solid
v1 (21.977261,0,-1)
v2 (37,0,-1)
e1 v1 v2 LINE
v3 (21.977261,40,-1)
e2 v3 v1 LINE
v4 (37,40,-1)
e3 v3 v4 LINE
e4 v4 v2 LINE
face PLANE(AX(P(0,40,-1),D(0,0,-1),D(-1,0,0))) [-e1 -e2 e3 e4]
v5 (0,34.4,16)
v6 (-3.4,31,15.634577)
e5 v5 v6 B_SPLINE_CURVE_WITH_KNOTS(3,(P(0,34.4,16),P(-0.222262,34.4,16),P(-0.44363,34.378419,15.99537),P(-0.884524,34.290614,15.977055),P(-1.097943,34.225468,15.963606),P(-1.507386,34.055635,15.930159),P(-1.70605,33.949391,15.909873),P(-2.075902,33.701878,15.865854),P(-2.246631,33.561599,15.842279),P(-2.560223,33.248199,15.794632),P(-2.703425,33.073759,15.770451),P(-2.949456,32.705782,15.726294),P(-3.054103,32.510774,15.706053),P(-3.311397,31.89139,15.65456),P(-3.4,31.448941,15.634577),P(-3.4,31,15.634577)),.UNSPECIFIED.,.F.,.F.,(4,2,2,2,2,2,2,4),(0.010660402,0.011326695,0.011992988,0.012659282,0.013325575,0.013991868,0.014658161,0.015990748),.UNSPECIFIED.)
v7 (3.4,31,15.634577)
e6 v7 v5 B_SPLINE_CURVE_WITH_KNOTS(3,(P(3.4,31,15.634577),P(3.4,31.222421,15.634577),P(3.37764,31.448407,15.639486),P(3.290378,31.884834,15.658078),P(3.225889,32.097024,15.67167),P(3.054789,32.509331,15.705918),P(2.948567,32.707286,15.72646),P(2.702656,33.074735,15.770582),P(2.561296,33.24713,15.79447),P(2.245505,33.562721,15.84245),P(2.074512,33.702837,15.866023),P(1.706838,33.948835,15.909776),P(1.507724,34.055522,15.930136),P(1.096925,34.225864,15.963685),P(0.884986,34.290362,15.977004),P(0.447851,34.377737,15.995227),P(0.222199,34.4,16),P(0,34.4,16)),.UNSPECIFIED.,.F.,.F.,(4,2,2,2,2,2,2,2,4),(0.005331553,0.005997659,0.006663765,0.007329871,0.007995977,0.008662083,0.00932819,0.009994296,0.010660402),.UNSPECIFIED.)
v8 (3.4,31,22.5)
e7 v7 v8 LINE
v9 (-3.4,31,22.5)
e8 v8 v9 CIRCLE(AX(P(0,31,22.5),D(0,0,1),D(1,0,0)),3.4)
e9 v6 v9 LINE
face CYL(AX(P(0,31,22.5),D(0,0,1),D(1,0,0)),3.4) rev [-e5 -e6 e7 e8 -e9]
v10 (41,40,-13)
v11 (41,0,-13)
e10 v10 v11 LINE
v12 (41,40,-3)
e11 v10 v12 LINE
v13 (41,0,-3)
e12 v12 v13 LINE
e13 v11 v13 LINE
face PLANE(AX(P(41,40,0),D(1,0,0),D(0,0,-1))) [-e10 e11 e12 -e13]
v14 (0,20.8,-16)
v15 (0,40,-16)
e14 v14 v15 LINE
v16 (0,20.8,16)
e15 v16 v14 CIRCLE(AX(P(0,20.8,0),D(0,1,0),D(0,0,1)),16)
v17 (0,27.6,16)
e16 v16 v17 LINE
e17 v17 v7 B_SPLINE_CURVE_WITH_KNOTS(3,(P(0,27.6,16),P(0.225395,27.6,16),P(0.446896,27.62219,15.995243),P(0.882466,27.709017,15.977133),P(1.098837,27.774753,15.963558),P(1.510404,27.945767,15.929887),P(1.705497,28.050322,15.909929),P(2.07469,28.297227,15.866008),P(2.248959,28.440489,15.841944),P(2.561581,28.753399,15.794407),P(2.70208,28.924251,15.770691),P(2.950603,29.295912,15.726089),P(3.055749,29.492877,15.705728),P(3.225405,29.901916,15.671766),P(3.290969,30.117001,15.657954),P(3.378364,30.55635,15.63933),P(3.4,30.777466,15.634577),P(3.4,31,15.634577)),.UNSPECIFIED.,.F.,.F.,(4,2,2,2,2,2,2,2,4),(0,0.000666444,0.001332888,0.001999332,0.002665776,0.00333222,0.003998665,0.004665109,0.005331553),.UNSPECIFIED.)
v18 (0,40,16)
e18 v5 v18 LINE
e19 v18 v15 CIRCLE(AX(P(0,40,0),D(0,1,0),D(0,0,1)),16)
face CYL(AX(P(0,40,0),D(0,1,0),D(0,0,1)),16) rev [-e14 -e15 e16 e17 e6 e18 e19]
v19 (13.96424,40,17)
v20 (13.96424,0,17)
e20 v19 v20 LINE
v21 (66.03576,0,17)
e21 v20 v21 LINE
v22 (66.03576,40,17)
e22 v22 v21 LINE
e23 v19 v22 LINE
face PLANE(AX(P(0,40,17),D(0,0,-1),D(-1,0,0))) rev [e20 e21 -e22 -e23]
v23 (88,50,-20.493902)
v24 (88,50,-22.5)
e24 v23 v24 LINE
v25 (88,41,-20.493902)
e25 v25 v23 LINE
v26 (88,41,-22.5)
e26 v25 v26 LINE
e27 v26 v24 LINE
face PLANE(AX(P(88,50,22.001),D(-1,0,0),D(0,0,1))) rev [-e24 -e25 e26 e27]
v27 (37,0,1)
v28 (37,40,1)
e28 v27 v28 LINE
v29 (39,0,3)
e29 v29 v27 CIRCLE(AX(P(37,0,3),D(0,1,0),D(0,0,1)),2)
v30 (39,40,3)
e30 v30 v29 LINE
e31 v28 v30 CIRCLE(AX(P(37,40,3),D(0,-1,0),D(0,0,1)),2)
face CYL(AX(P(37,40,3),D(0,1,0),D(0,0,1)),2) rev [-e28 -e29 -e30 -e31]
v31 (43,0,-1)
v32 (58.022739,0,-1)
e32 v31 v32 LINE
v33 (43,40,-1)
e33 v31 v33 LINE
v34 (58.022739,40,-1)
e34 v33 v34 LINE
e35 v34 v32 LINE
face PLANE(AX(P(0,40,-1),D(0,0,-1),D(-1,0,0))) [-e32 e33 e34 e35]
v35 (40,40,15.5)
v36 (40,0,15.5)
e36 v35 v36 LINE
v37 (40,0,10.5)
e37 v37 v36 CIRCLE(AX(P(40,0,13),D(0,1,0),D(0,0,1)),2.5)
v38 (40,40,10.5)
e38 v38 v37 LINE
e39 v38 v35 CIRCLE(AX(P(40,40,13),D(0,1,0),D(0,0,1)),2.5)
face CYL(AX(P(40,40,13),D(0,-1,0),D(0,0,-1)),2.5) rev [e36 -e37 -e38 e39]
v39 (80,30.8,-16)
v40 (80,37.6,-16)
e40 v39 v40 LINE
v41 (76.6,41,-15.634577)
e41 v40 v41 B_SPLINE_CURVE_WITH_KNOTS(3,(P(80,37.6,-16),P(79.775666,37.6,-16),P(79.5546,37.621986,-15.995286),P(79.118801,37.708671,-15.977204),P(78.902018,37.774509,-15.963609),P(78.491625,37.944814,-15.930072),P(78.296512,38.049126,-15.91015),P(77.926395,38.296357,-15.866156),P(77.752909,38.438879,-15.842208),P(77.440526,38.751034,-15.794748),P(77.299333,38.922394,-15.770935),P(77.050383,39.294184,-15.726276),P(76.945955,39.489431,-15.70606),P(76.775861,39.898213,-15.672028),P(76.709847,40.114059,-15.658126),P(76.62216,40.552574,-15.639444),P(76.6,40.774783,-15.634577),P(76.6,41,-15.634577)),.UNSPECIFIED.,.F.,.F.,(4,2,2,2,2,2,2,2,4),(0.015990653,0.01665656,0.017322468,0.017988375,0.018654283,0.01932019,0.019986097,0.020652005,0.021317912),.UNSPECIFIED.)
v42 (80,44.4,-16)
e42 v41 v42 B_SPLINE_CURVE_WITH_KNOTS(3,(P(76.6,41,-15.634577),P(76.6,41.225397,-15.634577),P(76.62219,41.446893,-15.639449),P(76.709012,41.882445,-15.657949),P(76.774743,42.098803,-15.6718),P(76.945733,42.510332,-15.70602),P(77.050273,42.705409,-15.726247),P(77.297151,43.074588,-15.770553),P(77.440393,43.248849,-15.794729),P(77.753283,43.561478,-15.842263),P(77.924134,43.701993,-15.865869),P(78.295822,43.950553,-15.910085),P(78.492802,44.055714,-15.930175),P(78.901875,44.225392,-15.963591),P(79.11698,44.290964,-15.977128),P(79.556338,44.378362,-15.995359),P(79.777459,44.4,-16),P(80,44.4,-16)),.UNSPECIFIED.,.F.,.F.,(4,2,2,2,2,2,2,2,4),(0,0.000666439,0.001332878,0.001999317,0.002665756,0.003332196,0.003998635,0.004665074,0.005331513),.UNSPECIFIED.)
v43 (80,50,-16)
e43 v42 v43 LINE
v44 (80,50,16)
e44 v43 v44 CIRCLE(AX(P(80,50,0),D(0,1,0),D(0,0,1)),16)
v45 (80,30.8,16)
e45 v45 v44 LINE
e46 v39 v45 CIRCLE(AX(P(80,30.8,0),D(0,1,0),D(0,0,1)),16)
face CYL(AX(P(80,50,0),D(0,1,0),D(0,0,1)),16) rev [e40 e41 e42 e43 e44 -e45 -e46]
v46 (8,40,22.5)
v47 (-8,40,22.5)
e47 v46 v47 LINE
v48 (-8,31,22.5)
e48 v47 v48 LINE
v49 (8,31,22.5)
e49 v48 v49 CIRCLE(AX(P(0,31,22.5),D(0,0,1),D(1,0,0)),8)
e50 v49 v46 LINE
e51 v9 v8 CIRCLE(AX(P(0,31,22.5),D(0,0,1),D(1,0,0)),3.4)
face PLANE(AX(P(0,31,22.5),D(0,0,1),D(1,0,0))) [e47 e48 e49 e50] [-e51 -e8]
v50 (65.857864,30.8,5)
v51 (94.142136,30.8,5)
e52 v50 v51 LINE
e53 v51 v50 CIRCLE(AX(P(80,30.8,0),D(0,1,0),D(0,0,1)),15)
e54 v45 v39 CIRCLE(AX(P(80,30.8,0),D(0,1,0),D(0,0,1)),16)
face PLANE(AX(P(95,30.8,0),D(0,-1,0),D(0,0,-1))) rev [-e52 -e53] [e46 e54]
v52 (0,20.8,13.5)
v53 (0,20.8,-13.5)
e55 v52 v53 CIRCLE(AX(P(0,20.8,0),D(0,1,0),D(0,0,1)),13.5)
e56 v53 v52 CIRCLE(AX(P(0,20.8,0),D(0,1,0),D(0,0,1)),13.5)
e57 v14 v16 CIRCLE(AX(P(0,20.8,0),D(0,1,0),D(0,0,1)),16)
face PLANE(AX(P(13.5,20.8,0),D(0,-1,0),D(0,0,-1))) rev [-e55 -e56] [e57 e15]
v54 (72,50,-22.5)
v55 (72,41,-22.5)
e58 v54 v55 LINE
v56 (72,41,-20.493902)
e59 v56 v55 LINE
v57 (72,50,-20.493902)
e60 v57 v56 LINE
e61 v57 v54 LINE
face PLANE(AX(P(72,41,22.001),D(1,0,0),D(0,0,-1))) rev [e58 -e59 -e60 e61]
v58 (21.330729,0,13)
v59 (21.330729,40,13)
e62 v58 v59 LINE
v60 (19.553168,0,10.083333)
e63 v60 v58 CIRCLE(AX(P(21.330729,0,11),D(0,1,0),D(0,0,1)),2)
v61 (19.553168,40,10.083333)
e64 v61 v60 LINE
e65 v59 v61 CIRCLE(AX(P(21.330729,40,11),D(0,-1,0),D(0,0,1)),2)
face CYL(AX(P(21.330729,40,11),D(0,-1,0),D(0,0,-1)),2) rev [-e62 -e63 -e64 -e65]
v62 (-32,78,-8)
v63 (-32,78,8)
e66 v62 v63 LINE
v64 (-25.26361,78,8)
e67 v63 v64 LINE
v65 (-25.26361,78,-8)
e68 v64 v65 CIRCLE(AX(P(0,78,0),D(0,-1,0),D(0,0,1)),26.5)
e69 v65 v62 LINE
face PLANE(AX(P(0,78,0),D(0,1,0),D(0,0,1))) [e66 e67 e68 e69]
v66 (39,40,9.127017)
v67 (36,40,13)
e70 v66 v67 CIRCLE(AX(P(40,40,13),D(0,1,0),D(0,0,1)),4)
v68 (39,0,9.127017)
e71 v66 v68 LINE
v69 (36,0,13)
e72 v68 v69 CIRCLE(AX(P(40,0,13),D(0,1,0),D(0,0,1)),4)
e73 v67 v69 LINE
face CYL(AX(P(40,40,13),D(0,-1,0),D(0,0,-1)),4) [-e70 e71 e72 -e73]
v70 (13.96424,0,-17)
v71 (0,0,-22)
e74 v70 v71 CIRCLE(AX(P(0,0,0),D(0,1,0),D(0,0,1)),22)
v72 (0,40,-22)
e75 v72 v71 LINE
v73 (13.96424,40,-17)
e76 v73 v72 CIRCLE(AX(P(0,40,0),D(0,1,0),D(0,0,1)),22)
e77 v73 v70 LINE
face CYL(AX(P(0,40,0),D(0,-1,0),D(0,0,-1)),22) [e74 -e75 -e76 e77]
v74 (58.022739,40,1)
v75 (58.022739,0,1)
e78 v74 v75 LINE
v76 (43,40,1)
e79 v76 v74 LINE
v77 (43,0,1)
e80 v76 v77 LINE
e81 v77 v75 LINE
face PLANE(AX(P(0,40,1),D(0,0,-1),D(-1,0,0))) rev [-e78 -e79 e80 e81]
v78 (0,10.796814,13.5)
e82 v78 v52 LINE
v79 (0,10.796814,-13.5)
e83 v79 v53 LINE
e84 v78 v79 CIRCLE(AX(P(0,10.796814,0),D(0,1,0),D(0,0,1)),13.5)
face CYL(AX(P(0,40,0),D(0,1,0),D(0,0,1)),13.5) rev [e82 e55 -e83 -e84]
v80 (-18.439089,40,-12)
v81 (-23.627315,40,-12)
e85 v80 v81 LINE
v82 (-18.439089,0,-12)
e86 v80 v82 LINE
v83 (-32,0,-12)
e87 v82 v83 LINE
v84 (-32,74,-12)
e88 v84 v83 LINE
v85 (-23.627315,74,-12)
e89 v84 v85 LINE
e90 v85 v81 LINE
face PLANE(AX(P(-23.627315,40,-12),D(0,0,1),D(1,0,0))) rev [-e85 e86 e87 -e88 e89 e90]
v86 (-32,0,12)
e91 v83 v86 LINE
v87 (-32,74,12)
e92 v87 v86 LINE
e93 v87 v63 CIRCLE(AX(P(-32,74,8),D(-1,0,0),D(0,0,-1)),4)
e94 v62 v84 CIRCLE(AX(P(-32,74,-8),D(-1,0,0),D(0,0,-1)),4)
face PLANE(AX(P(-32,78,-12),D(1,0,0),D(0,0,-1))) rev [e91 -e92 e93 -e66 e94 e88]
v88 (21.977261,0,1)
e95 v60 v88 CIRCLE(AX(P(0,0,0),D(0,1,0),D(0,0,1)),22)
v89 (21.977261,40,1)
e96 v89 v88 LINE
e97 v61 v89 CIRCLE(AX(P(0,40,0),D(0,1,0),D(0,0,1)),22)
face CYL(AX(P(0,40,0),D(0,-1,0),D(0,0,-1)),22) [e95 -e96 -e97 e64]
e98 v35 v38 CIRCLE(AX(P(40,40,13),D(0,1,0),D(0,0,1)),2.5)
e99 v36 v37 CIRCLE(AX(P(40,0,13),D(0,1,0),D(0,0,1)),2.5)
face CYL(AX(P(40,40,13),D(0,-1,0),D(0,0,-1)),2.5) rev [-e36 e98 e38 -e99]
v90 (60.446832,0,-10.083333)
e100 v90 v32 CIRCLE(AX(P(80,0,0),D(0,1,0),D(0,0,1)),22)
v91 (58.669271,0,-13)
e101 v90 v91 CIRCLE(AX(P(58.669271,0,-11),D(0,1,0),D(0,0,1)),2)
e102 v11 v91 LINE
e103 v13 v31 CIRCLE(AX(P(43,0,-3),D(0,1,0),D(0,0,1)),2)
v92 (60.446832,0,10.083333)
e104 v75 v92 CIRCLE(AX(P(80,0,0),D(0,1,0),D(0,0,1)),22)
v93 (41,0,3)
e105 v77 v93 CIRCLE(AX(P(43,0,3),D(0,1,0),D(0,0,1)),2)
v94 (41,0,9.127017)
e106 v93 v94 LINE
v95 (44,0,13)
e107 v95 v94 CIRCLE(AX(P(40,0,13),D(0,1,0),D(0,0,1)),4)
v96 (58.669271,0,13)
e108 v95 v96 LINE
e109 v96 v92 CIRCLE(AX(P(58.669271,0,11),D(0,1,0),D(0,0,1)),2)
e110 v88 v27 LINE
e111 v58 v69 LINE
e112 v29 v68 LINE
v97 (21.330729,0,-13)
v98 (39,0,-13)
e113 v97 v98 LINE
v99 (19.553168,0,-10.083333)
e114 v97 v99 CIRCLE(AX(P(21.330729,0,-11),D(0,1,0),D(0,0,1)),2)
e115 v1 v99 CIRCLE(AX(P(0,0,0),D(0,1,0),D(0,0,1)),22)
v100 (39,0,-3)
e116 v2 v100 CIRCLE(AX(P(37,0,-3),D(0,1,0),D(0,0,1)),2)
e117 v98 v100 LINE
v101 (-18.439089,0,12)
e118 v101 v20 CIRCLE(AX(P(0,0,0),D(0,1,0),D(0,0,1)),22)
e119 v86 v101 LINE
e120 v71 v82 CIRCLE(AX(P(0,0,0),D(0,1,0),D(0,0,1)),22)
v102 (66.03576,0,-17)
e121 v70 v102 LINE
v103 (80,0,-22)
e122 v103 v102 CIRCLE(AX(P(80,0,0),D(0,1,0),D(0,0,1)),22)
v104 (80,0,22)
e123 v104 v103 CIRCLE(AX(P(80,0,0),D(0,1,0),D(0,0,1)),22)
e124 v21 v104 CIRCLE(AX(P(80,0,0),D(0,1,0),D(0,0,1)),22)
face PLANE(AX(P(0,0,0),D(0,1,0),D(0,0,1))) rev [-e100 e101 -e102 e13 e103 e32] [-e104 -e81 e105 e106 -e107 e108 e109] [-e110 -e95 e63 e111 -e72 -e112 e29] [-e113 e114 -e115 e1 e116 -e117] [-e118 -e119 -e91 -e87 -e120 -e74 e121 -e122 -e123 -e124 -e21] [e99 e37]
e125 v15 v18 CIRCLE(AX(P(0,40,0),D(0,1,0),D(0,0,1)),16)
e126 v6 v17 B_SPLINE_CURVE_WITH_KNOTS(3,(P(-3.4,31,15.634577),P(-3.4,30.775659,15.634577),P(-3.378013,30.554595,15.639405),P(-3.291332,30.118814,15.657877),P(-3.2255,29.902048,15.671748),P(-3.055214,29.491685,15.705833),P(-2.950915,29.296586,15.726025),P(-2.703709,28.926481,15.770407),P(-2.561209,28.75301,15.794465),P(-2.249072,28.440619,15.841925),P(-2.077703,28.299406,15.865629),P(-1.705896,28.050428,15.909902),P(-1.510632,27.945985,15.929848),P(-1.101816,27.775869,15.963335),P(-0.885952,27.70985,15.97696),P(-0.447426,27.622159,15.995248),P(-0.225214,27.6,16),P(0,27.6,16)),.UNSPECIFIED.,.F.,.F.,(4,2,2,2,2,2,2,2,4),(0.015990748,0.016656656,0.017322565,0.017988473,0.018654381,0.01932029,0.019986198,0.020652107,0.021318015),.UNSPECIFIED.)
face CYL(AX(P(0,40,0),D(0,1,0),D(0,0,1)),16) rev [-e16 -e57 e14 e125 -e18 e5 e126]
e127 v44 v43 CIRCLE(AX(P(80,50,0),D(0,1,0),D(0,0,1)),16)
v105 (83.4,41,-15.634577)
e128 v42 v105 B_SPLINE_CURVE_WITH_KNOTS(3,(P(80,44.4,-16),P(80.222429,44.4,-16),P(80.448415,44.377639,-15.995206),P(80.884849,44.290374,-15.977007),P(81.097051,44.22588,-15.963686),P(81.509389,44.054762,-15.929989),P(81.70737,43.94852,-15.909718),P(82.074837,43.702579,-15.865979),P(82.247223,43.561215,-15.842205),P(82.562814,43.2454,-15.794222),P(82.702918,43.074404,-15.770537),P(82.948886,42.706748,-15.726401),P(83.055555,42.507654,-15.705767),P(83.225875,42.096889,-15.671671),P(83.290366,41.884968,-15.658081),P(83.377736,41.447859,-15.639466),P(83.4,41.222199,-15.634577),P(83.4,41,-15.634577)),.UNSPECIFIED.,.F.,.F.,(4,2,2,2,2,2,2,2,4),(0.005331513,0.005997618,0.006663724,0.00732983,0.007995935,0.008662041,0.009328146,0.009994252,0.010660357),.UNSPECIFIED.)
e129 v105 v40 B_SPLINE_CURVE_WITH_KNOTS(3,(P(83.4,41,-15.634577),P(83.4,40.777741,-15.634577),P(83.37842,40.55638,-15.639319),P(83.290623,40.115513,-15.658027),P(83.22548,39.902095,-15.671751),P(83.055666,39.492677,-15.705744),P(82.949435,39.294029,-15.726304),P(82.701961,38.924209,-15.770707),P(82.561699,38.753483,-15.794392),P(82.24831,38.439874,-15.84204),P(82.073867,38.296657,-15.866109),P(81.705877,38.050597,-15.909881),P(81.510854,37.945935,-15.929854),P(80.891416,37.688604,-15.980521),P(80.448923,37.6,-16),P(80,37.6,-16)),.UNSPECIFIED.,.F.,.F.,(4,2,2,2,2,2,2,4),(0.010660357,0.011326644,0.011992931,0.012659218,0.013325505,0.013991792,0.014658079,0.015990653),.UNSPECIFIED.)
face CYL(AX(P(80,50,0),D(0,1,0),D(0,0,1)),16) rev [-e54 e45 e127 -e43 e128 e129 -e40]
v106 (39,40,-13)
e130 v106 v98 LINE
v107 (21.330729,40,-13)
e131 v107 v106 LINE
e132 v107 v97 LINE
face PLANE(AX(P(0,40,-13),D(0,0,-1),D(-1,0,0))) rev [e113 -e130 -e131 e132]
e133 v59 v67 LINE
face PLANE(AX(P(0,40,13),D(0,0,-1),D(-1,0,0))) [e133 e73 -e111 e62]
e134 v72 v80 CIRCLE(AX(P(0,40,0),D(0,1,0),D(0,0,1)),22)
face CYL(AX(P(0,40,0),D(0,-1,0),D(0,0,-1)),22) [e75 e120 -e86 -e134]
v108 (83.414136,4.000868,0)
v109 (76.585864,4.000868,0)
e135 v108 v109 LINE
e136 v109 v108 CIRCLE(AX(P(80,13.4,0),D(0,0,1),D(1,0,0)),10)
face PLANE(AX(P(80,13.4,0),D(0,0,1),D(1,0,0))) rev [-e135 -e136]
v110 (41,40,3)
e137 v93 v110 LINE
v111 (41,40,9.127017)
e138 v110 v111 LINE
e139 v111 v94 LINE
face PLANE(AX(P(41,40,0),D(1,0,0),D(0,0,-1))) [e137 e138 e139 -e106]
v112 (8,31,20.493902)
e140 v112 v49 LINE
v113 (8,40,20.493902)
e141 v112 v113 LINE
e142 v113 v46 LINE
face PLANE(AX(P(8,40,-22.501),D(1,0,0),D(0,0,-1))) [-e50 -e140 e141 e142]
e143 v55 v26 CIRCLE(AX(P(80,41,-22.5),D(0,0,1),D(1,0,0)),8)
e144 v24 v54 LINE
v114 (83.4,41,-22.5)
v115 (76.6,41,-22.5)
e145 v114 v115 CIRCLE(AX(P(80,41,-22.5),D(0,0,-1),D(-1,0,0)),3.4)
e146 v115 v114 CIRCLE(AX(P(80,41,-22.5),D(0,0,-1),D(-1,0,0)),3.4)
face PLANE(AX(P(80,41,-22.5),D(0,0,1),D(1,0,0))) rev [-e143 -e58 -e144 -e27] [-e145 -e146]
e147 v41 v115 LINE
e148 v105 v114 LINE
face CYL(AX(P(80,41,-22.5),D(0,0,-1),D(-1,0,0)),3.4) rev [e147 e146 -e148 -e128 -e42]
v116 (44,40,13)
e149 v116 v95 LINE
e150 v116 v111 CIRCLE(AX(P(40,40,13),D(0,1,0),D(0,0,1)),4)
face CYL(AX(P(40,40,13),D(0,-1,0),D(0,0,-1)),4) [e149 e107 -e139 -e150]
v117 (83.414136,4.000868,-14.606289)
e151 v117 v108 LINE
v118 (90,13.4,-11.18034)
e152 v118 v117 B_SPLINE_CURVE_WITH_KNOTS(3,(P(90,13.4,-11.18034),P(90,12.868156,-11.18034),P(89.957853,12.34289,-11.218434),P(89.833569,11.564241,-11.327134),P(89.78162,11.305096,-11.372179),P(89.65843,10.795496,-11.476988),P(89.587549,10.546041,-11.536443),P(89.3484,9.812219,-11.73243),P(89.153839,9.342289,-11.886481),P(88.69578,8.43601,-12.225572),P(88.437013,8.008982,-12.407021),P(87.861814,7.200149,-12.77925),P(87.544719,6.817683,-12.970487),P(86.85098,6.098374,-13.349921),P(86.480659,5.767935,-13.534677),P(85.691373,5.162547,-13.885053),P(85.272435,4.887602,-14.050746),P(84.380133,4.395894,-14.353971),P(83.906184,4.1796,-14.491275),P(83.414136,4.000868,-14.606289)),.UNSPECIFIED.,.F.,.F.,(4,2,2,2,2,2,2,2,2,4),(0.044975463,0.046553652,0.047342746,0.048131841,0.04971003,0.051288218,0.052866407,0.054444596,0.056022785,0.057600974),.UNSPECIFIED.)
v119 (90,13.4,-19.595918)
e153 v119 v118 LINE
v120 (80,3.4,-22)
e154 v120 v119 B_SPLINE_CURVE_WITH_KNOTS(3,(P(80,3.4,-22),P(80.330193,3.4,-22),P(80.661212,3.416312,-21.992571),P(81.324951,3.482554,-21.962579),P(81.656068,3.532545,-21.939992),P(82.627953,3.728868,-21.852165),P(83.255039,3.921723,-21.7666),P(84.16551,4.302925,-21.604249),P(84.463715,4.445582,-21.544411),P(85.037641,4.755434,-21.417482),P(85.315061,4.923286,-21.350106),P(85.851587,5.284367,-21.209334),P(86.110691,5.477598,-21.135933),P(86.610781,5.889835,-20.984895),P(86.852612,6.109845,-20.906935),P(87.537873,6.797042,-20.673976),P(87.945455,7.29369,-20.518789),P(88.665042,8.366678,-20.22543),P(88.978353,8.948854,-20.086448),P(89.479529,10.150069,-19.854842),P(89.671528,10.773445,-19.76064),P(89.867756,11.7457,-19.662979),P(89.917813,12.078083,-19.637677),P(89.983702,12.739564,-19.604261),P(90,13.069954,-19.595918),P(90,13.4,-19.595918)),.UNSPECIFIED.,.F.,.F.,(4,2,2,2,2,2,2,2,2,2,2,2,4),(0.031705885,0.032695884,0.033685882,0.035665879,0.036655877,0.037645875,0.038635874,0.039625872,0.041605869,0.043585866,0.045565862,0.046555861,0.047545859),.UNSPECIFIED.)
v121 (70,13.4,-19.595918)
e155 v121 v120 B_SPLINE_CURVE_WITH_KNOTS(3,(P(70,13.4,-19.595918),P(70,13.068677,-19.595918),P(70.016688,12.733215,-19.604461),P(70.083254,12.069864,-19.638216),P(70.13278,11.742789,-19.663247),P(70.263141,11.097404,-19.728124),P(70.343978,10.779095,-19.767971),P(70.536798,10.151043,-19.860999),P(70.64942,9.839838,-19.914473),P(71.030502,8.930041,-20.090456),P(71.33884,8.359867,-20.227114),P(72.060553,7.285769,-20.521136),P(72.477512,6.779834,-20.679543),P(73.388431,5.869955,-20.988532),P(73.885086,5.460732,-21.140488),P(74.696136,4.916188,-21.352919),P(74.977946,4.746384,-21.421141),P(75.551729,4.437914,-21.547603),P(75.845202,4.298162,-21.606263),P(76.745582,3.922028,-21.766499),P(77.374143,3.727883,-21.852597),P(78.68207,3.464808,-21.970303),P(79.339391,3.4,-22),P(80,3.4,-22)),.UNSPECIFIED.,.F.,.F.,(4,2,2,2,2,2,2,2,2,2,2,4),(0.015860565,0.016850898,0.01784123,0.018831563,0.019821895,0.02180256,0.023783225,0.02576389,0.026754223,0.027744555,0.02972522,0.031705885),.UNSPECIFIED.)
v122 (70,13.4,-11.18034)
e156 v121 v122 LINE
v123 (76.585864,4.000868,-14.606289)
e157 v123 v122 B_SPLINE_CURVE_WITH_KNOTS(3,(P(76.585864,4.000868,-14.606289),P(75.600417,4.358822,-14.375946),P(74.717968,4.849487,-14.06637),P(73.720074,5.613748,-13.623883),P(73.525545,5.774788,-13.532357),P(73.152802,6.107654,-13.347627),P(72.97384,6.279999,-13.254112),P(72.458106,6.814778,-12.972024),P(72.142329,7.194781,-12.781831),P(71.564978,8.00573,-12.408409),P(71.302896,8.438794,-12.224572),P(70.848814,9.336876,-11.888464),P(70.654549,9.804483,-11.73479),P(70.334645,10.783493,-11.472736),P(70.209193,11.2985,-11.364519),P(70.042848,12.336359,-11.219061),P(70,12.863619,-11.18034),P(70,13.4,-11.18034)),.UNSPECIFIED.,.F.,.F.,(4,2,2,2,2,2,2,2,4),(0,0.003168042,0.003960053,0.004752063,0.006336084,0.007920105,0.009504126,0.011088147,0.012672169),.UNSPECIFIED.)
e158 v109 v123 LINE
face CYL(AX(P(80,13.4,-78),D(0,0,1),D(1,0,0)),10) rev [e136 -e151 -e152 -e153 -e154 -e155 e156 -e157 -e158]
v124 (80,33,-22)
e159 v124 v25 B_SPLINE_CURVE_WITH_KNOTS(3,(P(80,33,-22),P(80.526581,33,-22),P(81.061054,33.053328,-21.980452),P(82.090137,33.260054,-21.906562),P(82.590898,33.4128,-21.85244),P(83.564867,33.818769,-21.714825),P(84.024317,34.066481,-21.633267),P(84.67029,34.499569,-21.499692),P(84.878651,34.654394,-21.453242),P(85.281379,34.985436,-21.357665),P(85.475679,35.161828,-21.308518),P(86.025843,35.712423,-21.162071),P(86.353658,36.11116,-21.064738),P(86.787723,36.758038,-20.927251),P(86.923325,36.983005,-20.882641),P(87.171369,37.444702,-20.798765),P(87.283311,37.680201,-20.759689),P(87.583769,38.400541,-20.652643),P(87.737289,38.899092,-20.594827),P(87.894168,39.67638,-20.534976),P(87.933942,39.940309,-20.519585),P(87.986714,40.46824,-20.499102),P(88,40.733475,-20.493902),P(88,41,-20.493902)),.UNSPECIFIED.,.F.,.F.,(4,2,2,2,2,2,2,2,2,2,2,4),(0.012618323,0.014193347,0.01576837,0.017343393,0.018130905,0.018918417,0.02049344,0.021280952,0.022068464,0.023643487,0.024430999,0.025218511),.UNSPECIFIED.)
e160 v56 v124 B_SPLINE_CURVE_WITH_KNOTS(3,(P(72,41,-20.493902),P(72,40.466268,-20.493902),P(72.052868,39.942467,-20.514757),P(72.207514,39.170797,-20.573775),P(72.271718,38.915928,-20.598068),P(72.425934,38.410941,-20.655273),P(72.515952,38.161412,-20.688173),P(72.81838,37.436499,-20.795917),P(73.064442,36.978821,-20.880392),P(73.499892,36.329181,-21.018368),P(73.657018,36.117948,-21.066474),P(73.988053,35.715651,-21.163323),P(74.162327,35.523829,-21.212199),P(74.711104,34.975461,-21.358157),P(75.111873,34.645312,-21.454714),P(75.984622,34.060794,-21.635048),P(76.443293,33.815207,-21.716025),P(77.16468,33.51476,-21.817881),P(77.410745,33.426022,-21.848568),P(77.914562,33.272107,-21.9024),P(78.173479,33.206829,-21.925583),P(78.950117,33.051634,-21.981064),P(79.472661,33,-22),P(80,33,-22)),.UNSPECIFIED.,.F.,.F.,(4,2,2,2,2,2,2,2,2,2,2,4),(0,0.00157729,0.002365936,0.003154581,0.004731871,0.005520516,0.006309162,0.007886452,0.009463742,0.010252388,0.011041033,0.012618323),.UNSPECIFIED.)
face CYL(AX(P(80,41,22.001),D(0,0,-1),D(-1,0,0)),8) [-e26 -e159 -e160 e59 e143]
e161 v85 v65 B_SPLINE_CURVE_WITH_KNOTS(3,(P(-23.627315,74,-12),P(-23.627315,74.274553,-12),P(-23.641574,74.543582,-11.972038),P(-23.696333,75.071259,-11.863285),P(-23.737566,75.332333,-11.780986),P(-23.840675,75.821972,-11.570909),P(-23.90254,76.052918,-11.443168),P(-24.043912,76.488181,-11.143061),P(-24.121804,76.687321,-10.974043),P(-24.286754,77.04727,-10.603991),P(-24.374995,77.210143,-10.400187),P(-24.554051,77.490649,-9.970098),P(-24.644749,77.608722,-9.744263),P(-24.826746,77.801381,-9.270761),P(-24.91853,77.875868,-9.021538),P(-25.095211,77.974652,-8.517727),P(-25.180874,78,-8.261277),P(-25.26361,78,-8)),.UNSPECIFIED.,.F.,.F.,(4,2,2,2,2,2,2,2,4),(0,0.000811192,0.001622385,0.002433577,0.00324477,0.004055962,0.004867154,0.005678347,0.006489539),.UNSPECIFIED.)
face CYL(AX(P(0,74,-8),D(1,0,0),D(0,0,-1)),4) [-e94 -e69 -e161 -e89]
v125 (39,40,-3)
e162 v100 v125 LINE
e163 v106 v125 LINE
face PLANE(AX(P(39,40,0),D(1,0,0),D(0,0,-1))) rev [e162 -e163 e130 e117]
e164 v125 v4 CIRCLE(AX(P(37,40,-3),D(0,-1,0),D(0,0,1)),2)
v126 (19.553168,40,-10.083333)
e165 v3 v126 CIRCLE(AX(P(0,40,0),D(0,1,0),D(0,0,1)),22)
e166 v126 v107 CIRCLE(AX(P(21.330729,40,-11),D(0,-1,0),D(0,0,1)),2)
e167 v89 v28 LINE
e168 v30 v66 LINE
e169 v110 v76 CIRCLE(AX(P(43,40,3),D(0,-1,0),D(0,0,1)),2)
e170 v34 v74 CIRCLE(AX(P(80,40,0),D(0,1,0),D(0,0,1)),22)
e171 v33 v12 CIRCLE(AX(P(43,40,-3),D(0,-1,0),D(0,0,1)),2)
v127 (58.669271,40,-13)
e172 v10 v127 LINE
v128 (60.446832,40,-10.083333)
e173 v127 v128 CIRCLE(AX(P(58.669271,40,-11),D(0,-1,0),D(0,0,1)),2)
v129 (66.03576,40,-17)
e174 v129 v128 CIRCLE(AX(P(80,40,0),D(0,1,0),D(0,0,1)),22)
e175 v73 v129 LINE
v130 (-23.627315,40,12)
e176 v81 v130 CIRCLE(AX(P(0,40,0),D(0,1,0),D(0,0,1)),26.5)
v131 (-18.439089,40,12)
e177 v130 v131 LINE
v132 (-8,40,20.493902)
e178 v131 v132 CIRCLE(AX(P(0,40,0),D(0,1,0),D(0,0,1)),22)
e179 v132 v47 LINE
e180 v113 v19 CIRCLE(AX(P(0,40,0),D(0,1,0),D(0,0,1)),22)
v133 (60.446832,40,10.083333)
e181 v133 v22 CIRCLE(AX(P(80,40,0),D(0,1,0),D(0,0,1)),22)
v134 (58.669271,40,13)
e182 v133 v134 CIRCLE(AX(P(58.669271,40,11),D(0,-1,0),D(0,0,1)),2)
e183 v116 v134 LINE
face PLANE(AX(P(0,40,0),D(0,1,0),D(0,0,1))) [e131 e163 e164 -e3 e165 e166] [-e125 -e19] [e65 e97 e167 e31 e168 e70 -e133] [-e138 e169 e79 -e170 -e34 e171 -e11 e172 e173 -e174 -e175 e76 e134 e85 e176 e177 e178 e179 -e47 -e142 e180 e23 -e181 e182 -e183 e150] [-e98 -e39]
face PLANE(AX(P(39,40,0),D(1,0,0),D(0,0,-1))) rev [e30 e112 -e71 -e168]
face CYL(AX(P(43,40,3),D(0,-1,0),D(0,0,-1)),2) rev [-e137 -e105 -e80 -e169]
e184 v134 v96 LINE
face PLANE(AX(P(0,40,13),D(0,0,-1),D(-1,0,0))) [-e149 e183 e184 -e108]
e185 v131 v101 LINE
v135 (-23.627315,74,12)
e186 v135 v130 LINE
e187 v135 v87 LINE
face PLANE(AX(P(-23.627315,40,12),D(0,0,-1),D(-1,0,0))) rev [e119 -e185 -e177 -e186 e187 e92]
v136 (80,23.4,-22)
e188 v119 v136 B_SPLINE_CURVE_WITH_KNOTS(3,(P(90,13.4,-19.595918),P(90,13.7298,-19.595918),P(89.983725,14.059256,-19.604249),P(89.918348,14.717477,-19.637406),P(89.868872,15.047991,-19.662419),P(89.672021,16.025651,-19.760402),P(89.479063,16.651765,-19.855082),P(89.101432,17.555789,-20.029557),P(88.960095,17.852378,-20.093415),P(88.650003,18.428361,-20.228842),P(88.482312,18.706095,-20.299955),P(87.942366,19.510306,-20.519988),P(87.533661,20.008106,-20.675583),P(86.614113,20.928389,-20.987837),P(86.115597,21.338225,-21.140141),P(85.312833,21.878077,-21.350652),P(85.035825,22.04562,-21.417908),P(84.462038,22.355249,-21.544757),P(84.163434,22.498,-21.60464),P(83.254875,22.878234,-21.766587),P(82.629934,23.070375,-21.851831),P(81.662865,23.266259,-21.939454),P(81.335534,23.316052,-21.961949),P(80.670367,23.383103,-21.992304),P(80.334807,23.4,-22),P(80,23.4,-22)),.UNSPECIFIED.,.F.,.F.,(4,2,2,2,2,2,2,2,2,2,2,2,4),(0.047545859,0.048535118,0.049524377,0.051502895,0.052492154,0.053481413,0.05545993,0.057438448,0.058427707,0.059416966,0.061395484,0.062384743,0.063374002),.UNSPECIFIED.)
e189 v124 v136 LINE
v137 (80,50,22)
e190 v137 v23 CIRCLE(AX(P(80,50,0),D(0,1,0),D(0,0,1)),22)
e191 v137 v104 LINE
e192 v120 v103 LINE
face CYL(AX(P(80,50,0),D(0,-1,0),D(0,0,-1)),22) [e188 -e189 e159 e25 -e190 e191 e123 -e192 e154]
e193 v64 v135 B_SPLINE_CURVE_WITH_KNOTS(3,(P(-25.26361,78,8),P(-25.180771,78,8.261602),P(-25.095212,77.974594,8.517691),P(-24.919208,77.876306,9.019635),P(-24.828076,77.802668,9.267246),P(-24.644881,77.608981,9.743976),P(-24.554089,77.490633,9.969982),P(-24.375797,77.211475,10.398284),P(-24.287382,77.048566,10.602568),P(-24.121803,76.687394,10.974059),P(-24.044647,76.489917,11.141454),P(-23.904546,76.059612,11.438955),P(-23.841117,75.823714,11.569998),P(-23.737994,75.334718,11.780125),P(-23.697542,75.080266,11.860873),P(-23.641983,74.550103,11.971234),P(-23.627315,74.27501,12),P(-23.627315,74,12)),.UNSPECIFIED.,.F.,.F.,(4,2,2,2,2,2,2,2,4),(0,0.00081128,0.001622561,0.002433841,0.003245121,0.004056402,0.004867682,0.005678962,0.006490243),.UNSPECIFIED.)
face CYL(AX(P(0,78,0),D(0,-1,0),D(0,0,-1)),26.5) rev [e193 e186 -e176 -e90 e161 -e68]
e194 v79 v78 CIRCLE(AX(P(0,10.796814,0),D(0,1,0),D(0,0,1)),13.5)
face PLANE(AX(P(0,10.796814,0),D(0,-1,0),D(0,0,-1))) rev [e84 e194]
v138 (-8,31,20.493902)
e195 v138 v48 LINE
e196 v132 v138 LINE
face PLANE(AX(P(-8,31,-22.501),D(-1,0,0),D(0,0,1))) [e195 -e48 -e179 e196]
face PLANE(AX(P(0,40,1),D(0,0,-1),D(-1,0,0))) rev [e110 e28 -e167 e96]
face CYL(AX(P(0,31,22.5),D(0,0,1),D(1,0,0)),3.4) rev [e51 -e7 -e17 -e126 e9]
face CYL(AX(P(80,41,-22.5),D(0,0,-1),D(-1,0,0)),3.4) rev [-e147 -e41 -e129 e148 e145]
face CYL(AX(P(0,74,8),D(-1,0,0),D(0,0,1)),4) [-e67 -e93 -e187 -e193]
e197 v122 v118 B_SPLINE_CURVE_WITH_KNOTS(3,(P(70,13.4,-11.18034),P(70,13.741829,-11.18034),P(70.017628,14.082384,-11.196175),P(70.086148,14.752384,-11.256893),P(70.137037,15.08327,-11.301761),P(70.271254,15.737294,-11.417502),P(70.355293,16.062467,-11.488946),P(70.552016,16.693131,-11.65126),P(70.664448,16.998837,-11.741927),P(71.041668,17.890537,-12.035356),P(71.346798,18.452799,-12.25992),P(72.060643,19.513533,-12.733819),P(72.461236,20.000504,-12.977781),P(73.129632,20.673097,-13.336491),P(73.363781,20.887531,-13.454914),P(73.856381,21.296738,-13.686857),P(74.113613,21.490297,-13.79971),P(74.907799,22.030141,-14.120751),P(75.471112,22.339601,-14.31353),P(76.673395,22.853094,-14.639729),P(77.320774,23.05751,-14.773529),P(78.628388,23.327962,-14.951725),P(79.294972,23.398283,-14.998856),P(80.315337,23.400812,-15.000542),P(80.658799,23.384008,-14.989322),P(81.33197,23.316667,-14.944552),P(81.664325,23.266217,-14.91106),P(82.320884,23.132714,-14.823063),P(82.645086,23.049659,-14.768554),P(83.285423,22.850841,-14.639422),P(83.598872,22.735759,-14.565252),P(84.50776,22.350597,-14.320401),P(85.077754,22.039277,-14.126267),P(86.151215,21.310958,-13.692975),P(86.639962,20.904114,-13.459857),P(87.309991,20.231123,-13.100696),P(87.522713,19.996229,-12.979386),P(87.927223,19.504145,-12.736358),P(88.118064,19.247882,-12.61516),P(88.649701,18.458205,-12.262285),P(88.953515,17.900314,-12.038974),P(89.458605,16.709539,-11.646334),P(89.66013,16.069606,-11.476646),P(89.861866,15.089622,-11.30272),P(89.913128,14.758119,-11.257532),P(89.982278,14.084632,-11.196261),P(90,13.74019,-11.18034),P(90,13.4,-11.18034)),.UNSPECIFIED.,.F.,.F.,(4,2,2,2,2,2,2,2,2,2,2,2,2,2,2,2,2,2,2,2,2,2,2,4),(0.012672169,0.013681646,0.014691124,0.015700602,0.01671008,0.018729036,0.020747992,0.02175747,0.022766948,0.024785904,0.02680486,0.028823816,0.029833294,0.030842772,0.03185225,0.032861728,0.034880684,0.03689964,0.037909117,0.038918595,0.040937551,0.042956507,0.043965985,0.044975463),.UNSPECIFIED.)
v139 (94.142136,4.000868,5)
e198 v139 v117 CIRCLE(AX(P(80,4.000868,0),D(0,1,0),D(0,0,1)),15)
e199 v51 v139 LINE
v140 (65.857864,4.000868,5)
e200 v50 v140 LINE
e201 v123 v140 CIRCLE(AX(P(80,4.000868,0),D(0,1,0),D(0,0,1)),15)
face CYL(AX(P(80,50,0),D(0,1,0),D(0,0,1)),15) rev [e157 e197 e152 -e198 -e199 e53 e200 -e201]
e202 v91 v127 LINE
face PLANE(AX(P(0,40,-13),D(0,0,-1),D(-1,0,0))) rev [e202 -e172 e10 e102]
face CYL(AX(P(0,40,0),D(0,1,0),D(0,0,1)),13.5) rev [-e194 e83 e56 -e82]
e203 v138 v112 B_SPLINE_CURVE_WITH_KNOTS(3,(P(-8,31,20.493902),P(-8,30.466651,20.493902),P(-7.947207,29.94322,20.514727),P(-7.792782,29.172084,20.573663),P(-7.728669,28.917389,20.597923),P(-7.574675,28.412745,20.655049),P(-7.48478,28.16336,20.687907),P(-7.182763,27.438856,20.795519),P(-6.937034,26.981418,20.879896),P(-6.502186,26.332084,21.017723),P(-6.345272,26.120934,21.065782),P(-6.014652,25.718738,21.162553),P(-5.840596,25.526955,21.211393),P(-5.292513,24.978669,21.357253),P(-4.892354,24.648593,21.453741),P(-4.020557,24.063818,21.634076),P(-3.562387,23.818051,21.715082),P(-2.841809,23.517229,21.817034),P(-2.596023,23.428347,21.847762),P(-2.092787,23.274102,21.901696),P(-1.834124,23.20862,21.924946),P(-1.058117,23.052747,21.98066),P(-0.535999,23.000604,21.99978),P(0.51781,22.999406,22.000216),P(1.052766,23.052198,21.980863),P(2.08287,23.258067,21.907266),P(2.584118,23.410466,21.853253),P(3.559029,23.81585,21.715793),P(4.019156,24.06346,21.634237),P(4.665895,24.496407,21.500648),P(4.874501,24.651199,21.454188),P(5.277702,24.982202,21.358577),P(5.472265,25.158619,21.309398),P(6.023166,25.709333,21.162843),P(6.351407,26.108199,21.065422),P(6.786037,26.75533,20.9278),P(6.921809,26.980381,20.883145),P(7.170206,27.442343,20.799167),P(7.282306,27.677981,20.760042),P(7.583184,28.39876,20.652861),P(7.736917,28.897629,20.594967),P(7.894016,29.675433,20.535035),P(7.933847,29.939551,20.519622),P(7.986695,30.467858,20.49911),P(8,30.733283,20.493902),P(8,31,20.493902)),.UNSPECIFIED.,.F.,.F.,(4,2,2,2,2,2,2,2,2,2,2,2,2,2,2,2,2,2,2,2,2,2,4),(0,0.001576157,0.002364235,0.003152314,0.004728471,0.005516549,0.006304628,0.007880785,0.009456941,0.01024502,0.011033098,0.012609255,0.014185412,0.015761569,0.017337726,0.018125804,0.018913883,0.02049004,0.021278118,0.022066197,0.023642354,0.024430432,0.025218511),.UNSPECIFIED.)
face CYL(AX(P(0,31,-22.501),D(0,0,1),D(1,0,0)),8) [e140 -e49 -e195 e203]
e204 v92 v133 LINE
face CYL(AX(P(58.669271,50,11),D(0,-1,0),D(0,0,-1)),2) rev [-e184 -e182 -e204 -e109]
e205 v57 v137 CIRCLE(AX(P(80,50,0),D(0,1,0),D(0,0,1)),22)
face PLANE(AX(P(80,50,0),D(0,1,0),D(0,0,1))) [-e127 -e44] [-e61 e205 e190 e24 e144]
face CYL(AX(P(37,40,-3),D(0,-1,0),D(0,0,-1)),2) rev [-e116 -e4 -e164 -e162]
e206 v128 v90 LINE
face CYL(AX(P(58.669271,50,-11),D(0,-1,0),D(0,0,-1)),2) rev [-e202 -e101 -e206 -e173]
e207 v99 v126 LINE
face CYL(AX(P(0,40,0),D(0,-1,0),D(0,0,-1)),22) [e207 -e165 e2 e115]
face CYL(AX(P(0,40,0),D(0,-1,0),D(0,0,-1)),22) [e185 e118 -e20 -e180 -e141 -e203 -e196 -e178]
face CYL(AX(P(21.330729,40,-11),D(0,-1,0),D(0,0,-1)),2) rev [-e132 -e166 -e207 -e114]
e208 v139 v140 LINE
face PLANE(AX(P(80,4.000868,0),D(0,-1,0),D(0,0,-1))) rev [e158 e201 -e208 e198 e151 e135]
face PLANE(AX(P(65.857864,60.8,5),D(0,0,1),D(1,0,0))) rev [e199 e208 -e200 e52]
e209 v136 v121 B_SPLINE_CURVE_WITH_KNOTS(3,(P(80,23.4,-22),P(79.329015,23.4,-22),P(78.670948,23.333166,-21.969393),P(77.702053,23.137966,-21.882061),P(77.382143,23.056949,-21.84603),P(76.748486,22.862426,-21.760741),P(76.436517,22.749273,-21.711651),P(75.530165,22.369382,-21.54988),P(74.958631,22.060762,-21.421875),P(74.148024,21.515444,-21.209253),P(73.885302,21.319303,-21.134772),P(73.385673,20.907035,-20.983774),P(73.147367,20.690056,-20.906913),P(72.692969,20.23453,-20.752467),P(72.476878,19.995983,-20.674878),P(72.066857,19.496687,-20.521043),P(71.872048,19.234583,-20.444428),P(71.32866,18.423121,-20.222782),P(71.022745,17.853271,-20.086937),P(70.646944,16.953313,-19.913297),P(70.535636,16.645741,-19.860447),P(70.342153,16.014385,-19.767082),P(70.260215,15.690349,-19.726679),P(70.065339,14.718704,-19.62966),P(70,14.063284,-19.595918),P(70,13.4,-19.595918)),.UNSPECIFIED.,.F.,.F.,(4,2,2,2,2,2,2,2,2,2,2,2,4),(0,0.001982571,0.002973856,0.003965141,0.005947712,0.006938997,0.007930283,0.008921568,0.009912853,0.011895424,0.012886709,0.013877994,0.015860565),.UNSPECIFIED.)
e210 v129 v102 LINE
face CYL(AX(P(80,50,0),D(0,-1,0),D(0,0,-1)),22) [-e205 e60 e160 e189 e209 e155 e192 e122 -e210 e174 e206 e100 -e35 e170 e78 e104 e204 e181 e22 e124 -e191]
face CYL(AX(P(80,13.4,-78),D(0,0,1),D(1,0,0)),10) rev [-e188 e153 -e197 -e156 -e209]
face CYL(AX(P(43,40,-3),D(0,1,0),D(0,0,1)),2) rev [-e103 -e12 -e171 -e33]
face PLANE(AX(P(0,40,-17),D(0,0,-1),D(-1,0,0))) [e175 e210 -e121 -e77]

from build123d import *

# Parameters (mm, degrees)
HUB_1_DEPTH                          = 40
HUB_2_SKETCH_R                       = 22
HUB_2_DEPTH                          = 50
RIBBED_WEB_SKETCH_R                  = 2.5
RIBBED_WEB_DEPTH                     = 40
WEB_FILLETS_R2_R                     = 2
HUB_1_BORE_27_CBORE_32_D             = 27
HUB_1_BORE_27_CBORE_32_DEPTH         = 29.20318647
HUB_1_BORE_27_CBORE_32_CBORE_D       = 32
HUB_1_BORE_27_CBORE_32_CBORE_DEPTH   = 19.2
UPRIGHT_TAB_DEPTH                    = 78
TAB_FILLETS_R4_R                     = 4
HUB_2_BORE_30_CBORE_32_D             = 30
HUB_2_BORE_30_CBORE_32_DEPTH         = 45.999131514
HUB_2_BORE_30_CBORE_32_CBORE_D       = 32
HUB_2_BORE_30_CBORE_32_CBORE_DEPTH   = 19.2
CLEARANCE_CUT_SKETCH_R               = 10
CLEARANCE_CUT_DEPTH                  = 78
HUB_2_SET_SCREW_BOSS_REACH           = 137.898
HUB_2_SET_SCREW_BOSS_END_RADIUS      = 22
HUB_1_SET_SCREW_BOSS_REACH           = 138.062
HUB_1_SET_SCREW_BOSS_END_RADIUS      = 22
M8X1_25_TAPPED_HOLE1_REACH           = 129.475
M8X1_25_TAPPED_HOLE1_BORE_R          = 3.4
M8X1_25_TAPPED_HOLE1_ON_FACE_2_REACH = 122.988
M8X1_25_TAPPED_HOLE1_BORE_2_R        = 3.4
WEB_BOSS_DEPTH                       = 26.799131514


with BuildPart() as part:
    # Hub 1 Sketch → Hub 1 (new body)
    with BuildSketch(Plane(origin=(0, 0, 0), x_dir=(1, 0, 0), z_dir=(0, 1, 0))):
        with BuildLine():
            Line((-23.627314701, 12), (-18.439088915, 12))
            ThreePointArc((-18.439088915, 12), (22, 0), (-18.439088915, -12))
            Line((-18.439088915, -12), (-23.627314701, -12))
            ThreePointArc((-23.627314701, -12), (-26.5, 0), (-23.627314701, 12))
        make_face()
    extrude(amount=HUB_1_DEPTH)



with BuildPart() as body_2:
    # Hub 2 Sketch → Hub 2 (new body)
    with BuildSketch(Plane(origin=(0, 0, 0), x_dir=(1, 0, 0), z_dir=(0, 1, 0))):
        with Locations(Location((80, 0, 0), (0, 0, 270))):
            Circle(HUB_2_SKETCH_R)
    extrude(amount=HUB_2_DEPTH)


with BuildPart() as part_1:
    add(part.part)

    add(body_2.part)  # Ribbed Web merges body 2
    # Ribbed Web Sketch → Ribbed Web (add)
    with BuildSketch(Plane(origin=(0, 0, 0), x_dir=(1, 0, 0), z_dir=(0, 1, 0))):
        with BuildLine():
            Line((39, -1), (39, -9.127016654))
            ThreePointArc((39, -9.127016654), (36.83772234, -10.550510257), (36, -13))
            Line((36, -13), (17.748239349, -13))
            ThreePointArc((17.748239349, -13), (15.981875275, -15.118851236), (13.964240044, -17))
            Line((13.964240044, -17), (66.035759956, -17))
            ThreePointArc((66.035759956, -17), (64.018124725, -15.118851236), (62.251760651, -13))
            Line((62.251760651, -13), (44, -13))
            ThreePointArc((44, -13), (43.16227766, -10.550510257), (41, -9.127016654))
            Line((41, -9.127016654), (41, -1))
            Line((41, -1), (58.022739024, -1))
            ThreePointArc((58.022739024, -1), (58, 0), (58.022739024, 1))
            Line((58.022739024, 1), (41, 1))
            Line((41, 1), (41, 13))
            Line((41, 13), (62.251760651, 13))
            ThreePointArc((62.251760651, 13), (64.018124725, 15.118851236), (66.035759956, 17))
            Line((66.035759956, 17), (13.964240044, 17))
            ThreePointArc((13.964240044, 17), (15.981875275, 15.118851236), (17.748239349, 13))
            Line((17.748239349, 13), (39, 13))
            Line((39, 13), (39, 1))
            Line((39, 1), (21.977260976, 1))
            ThreePointArc((21.977260976, 1), (22, 0), (21.977260976, -1))
            Line((21.977260976, -1), (39, -1))
        make_face()
        with Locations(Location((40, -13, 0), (0, 0, 270))):
            Circle(RIBBED_WEB_SKETCH_R, mode=Mode.SUBTRACT)
    extrude(amount=RIBBED_WEB_DEPTH)

    # Web Fillets R2
    web_fillets_r2_edges = [part_1.edges().sort_by_distance(p)[0] for p in [
        (39, 20, 1),
        (17.748239349, 20, 13),
        (62.251760651, 20, 13),
        (41, 20, 1),
        (41, 20, -1),
        (62.251760651, 20, -13),
        (17.748239349, 20, -13),
        (39, 20, -1),
    ]]
    fillet(web_fillets_r2_edges, radius=WEB_FILLETS_R2_R)

    # Hub 1 Bore Ø27 CBore Ø32
    with Locations(Plane.ZX.offset(40)):
        with Locations((0, 0)):
            CounterBoreHole(HUB_1_BORE_27_CBORE_32_D / 2, HUB_1_BORE_27_CBORE_32_CBORE_D / 2, HUB_1_BORE_27_CBORE_32_CBORE_DEPTH, depth=HUB_1_BORE_27_CBORE_32_DEPTH)

    # Upright Tab Sketch → Upright Tab (add)
    with BuildSketch(Plane(origin=(0, 0, 0), x_dir=(1, 0, 0), z_dir=(0, 1, 0))):
        with BuildLine():
            Line((-23.627314701, 12), (-32, 12))
            Line((-32, 12), (-32, -12))
            Line((-32, -12), (-23.627314701, -12))
            ThreePointArc((-23.627314701, -12), (-26.5, 0), (-23.627314701, 12))
        make_face()
    extrude(amount=UPRIGHT_TAB_DEPTH)

    # Tab Fillets R4
    tab_fillets_r4_edges = [part_1.edges().sort_by_distance(p)[0] for p in [
        (-27.813657351, 78, -12),
        (-27.813657351, 78, 12),
    ]]
    fillet(tab_fillets_r4_edges, radius=TAB_FILLETS_R4_R)

    # Hub 2 Bore Ø30 CBore Ø32
    with Locations(Plane(origin=(80, 50, 0), x_dir=(0, 0, 1), z_dir=(0, 1, 0))):
        with Locations((0, 0)):
            CounterBoreHole(HUB_2_BORE_30_CBORE_32_D / 2, HUB_2_BORE_30_CBORE_32_CBORE_D / 2, HUB_2_BORE_30_CBORE_32_CBORE_DEPTH, depth=HUB_2_BORE_30_CBORE_32_DEPTH)

    # Clearance Cut Sketch → Clearance Cut (cut)
    with BuildSketch(Plane.XY):
        with Locations(Location((80, 13.4, 0), (0, 0, 289.963023571))):
            Circle(CLEARANCE_CUT_SKETCH_R)
    extrude(amount=-CLEARANCE_CUT_DEPTH, mode=Mode.SUBTRACT)

    # Hub 2 Set Screw Boss: up to this cylinder (the profile starts outside it)
    hub_2_set_screw_boss_end = Plane(origin=(80, 42.254102, 0), z_dir=(0, -1, 0)) * Cylinder(HUB_2_SET_SCREW_BOSS_END_RADIUS, 320.796, mode=Mode.PRIVATE)
    # Hub 2 Set Screw Boss Sketch → Hub 2 Set Screw Boss (add, up to the surface)
    with BuildSketch(Plane.XY.offset(-22.5), mode=Mode.PRIVATE) as hub_2_set_screw_boss_sk1:
        with BuildLine():
            Line((72, 41), (72, 50))
            Line((72, 50), (88, 50))
            Line((88, 50), (88, 41))
            ThreePointArc((88, 41), (80, 33), (72, 41))
        make_face()
    hub_2_set_screw_boss_tool1 = extrude(hub_2_set_screw_boss_sk1.sketch, amount=HUB_2_SET_SCREW_BOSS_REACH, mode=Mode.PRIVATE) - hub_2_set_screw_boss_end
    add(hub_2_set_screw_boss_tool1.solids().sort_by_distance((80, 42.254102, -22.5))[0])

    # Hub 1 Set Screw Boss: up to this cylinder (the profile starts outside it)
    hub_1_set_screw_boss_end = Plane(origin=(0, 32.254102, 0), z_dir=(0, -1, 0)) * Cylinder(HUB_1_SET_SCREW_BOSS_END_RADIUS, 321.124, mode=Mode.PRIVATE)
    # Hub 1 Set Screw Boss Sketch → Hub 1 Set Screw Boss (add, up to the surface)
    with BuildSketch(Plane.XY.offset(22.5), mode=Mode.PRIVATE) as hub_1_set_screw_boss_sk1:
        with BuildLine():
            Line((-8, 31), (-8, 40))
            Line((-8, 40), (8, 40))
            Line((8, 40), (8, 31))
            ThreePointArc((8, 31), (0, 23), (-8, 31))
        make_face()
    hub_1_set_screw_boss_tool1 = extrude(hub_1_set_screw_boss_sk1.sketch, amount=-HUB_1_SET_SCREW_BOSS_REACH, mode=Mode.PRIVATE) - hub_1_set_screw_boss_end
    add(hub_1_set_screw_boss_tool1.solids().sort_by_distance((0, 32.254102, 22.5))[0])

    # M8x1.25 Tapped Hole1 bore (on position points) → M8x1.25 Tapped Hole1 (cut, up to next)
    with BuildSketch(Plane(origin=(80, 41, -22.5), x_dir=(-1, 0, 0), z_dir=(0, 0, -1)), mode=Mode.PRIVATE) as m8x1_25_tapped_hole1_sk1:
        Circle(M8X1_25_TAPPED_HOLE1_BORE_R)
    m8x1_25_tapped_hole1_tool1 = extrude(m8x1_25_tapped_hole1_sk1.sketch, amount=-M8X1_25_TAPPED_HOLE1_REACH, mode=Mode.PRIVATE) & part_1.part
    add(m8x1_25_tapped_hole1_tool1.solids().sort_by_distance((80, 41, -22.5))[0], mode=Mode.SUBTRACT)

    # M8x1.25 Tapped Hole1 bore 2 (on position points) → M8x1.25 Tapped Hole1 on face 2 (cut, up to next)
    with BuildSketch(Plane(origin=(0, 31, 22.5), x_dir=(1, 0, 0), z_dir=(0, 0, 1)), mode=Mode.PRIVATE) as m8x1_25_tapped_hole1_on_face_2_sk1:
        Circle(M8X1_25_TAPPED_HOLE1_BORE_2_R)
    m8x1_25_tapped_hole1_on_face_2_tool1 = extrude(m8x1_25_tapped_hole1_on_face_2_sk1.sketch, amount=-M8X1_25_TAPPED_HOLE1_ON_FACE_2_REACH, mode=Mode.PRIVATE) & part_1.part
    add(m8x1_25_tapped_hole1_on_face_2_tool1.solids().sort_by_distance((0, 31, 22.5))[0], mode=Mode.SUBTRACT)

    # Web Boss Sketch → Web Boss (add)
    with BuildSketch(Plane(origin=(0, 4.000868486, 0), x_dir=(1, 0, 0), z_dir=(0, 1, 0))):
        with BuildLine():
            Line((65.857864376, -5), (94.142135624, -5))
            ThreePointArc((94.142135624, -5), (80, -15), (65.857864376, -5))
        make_face()
    extrude(amount=WEB_BOSS_DEPTH)


solid = part_1.part
